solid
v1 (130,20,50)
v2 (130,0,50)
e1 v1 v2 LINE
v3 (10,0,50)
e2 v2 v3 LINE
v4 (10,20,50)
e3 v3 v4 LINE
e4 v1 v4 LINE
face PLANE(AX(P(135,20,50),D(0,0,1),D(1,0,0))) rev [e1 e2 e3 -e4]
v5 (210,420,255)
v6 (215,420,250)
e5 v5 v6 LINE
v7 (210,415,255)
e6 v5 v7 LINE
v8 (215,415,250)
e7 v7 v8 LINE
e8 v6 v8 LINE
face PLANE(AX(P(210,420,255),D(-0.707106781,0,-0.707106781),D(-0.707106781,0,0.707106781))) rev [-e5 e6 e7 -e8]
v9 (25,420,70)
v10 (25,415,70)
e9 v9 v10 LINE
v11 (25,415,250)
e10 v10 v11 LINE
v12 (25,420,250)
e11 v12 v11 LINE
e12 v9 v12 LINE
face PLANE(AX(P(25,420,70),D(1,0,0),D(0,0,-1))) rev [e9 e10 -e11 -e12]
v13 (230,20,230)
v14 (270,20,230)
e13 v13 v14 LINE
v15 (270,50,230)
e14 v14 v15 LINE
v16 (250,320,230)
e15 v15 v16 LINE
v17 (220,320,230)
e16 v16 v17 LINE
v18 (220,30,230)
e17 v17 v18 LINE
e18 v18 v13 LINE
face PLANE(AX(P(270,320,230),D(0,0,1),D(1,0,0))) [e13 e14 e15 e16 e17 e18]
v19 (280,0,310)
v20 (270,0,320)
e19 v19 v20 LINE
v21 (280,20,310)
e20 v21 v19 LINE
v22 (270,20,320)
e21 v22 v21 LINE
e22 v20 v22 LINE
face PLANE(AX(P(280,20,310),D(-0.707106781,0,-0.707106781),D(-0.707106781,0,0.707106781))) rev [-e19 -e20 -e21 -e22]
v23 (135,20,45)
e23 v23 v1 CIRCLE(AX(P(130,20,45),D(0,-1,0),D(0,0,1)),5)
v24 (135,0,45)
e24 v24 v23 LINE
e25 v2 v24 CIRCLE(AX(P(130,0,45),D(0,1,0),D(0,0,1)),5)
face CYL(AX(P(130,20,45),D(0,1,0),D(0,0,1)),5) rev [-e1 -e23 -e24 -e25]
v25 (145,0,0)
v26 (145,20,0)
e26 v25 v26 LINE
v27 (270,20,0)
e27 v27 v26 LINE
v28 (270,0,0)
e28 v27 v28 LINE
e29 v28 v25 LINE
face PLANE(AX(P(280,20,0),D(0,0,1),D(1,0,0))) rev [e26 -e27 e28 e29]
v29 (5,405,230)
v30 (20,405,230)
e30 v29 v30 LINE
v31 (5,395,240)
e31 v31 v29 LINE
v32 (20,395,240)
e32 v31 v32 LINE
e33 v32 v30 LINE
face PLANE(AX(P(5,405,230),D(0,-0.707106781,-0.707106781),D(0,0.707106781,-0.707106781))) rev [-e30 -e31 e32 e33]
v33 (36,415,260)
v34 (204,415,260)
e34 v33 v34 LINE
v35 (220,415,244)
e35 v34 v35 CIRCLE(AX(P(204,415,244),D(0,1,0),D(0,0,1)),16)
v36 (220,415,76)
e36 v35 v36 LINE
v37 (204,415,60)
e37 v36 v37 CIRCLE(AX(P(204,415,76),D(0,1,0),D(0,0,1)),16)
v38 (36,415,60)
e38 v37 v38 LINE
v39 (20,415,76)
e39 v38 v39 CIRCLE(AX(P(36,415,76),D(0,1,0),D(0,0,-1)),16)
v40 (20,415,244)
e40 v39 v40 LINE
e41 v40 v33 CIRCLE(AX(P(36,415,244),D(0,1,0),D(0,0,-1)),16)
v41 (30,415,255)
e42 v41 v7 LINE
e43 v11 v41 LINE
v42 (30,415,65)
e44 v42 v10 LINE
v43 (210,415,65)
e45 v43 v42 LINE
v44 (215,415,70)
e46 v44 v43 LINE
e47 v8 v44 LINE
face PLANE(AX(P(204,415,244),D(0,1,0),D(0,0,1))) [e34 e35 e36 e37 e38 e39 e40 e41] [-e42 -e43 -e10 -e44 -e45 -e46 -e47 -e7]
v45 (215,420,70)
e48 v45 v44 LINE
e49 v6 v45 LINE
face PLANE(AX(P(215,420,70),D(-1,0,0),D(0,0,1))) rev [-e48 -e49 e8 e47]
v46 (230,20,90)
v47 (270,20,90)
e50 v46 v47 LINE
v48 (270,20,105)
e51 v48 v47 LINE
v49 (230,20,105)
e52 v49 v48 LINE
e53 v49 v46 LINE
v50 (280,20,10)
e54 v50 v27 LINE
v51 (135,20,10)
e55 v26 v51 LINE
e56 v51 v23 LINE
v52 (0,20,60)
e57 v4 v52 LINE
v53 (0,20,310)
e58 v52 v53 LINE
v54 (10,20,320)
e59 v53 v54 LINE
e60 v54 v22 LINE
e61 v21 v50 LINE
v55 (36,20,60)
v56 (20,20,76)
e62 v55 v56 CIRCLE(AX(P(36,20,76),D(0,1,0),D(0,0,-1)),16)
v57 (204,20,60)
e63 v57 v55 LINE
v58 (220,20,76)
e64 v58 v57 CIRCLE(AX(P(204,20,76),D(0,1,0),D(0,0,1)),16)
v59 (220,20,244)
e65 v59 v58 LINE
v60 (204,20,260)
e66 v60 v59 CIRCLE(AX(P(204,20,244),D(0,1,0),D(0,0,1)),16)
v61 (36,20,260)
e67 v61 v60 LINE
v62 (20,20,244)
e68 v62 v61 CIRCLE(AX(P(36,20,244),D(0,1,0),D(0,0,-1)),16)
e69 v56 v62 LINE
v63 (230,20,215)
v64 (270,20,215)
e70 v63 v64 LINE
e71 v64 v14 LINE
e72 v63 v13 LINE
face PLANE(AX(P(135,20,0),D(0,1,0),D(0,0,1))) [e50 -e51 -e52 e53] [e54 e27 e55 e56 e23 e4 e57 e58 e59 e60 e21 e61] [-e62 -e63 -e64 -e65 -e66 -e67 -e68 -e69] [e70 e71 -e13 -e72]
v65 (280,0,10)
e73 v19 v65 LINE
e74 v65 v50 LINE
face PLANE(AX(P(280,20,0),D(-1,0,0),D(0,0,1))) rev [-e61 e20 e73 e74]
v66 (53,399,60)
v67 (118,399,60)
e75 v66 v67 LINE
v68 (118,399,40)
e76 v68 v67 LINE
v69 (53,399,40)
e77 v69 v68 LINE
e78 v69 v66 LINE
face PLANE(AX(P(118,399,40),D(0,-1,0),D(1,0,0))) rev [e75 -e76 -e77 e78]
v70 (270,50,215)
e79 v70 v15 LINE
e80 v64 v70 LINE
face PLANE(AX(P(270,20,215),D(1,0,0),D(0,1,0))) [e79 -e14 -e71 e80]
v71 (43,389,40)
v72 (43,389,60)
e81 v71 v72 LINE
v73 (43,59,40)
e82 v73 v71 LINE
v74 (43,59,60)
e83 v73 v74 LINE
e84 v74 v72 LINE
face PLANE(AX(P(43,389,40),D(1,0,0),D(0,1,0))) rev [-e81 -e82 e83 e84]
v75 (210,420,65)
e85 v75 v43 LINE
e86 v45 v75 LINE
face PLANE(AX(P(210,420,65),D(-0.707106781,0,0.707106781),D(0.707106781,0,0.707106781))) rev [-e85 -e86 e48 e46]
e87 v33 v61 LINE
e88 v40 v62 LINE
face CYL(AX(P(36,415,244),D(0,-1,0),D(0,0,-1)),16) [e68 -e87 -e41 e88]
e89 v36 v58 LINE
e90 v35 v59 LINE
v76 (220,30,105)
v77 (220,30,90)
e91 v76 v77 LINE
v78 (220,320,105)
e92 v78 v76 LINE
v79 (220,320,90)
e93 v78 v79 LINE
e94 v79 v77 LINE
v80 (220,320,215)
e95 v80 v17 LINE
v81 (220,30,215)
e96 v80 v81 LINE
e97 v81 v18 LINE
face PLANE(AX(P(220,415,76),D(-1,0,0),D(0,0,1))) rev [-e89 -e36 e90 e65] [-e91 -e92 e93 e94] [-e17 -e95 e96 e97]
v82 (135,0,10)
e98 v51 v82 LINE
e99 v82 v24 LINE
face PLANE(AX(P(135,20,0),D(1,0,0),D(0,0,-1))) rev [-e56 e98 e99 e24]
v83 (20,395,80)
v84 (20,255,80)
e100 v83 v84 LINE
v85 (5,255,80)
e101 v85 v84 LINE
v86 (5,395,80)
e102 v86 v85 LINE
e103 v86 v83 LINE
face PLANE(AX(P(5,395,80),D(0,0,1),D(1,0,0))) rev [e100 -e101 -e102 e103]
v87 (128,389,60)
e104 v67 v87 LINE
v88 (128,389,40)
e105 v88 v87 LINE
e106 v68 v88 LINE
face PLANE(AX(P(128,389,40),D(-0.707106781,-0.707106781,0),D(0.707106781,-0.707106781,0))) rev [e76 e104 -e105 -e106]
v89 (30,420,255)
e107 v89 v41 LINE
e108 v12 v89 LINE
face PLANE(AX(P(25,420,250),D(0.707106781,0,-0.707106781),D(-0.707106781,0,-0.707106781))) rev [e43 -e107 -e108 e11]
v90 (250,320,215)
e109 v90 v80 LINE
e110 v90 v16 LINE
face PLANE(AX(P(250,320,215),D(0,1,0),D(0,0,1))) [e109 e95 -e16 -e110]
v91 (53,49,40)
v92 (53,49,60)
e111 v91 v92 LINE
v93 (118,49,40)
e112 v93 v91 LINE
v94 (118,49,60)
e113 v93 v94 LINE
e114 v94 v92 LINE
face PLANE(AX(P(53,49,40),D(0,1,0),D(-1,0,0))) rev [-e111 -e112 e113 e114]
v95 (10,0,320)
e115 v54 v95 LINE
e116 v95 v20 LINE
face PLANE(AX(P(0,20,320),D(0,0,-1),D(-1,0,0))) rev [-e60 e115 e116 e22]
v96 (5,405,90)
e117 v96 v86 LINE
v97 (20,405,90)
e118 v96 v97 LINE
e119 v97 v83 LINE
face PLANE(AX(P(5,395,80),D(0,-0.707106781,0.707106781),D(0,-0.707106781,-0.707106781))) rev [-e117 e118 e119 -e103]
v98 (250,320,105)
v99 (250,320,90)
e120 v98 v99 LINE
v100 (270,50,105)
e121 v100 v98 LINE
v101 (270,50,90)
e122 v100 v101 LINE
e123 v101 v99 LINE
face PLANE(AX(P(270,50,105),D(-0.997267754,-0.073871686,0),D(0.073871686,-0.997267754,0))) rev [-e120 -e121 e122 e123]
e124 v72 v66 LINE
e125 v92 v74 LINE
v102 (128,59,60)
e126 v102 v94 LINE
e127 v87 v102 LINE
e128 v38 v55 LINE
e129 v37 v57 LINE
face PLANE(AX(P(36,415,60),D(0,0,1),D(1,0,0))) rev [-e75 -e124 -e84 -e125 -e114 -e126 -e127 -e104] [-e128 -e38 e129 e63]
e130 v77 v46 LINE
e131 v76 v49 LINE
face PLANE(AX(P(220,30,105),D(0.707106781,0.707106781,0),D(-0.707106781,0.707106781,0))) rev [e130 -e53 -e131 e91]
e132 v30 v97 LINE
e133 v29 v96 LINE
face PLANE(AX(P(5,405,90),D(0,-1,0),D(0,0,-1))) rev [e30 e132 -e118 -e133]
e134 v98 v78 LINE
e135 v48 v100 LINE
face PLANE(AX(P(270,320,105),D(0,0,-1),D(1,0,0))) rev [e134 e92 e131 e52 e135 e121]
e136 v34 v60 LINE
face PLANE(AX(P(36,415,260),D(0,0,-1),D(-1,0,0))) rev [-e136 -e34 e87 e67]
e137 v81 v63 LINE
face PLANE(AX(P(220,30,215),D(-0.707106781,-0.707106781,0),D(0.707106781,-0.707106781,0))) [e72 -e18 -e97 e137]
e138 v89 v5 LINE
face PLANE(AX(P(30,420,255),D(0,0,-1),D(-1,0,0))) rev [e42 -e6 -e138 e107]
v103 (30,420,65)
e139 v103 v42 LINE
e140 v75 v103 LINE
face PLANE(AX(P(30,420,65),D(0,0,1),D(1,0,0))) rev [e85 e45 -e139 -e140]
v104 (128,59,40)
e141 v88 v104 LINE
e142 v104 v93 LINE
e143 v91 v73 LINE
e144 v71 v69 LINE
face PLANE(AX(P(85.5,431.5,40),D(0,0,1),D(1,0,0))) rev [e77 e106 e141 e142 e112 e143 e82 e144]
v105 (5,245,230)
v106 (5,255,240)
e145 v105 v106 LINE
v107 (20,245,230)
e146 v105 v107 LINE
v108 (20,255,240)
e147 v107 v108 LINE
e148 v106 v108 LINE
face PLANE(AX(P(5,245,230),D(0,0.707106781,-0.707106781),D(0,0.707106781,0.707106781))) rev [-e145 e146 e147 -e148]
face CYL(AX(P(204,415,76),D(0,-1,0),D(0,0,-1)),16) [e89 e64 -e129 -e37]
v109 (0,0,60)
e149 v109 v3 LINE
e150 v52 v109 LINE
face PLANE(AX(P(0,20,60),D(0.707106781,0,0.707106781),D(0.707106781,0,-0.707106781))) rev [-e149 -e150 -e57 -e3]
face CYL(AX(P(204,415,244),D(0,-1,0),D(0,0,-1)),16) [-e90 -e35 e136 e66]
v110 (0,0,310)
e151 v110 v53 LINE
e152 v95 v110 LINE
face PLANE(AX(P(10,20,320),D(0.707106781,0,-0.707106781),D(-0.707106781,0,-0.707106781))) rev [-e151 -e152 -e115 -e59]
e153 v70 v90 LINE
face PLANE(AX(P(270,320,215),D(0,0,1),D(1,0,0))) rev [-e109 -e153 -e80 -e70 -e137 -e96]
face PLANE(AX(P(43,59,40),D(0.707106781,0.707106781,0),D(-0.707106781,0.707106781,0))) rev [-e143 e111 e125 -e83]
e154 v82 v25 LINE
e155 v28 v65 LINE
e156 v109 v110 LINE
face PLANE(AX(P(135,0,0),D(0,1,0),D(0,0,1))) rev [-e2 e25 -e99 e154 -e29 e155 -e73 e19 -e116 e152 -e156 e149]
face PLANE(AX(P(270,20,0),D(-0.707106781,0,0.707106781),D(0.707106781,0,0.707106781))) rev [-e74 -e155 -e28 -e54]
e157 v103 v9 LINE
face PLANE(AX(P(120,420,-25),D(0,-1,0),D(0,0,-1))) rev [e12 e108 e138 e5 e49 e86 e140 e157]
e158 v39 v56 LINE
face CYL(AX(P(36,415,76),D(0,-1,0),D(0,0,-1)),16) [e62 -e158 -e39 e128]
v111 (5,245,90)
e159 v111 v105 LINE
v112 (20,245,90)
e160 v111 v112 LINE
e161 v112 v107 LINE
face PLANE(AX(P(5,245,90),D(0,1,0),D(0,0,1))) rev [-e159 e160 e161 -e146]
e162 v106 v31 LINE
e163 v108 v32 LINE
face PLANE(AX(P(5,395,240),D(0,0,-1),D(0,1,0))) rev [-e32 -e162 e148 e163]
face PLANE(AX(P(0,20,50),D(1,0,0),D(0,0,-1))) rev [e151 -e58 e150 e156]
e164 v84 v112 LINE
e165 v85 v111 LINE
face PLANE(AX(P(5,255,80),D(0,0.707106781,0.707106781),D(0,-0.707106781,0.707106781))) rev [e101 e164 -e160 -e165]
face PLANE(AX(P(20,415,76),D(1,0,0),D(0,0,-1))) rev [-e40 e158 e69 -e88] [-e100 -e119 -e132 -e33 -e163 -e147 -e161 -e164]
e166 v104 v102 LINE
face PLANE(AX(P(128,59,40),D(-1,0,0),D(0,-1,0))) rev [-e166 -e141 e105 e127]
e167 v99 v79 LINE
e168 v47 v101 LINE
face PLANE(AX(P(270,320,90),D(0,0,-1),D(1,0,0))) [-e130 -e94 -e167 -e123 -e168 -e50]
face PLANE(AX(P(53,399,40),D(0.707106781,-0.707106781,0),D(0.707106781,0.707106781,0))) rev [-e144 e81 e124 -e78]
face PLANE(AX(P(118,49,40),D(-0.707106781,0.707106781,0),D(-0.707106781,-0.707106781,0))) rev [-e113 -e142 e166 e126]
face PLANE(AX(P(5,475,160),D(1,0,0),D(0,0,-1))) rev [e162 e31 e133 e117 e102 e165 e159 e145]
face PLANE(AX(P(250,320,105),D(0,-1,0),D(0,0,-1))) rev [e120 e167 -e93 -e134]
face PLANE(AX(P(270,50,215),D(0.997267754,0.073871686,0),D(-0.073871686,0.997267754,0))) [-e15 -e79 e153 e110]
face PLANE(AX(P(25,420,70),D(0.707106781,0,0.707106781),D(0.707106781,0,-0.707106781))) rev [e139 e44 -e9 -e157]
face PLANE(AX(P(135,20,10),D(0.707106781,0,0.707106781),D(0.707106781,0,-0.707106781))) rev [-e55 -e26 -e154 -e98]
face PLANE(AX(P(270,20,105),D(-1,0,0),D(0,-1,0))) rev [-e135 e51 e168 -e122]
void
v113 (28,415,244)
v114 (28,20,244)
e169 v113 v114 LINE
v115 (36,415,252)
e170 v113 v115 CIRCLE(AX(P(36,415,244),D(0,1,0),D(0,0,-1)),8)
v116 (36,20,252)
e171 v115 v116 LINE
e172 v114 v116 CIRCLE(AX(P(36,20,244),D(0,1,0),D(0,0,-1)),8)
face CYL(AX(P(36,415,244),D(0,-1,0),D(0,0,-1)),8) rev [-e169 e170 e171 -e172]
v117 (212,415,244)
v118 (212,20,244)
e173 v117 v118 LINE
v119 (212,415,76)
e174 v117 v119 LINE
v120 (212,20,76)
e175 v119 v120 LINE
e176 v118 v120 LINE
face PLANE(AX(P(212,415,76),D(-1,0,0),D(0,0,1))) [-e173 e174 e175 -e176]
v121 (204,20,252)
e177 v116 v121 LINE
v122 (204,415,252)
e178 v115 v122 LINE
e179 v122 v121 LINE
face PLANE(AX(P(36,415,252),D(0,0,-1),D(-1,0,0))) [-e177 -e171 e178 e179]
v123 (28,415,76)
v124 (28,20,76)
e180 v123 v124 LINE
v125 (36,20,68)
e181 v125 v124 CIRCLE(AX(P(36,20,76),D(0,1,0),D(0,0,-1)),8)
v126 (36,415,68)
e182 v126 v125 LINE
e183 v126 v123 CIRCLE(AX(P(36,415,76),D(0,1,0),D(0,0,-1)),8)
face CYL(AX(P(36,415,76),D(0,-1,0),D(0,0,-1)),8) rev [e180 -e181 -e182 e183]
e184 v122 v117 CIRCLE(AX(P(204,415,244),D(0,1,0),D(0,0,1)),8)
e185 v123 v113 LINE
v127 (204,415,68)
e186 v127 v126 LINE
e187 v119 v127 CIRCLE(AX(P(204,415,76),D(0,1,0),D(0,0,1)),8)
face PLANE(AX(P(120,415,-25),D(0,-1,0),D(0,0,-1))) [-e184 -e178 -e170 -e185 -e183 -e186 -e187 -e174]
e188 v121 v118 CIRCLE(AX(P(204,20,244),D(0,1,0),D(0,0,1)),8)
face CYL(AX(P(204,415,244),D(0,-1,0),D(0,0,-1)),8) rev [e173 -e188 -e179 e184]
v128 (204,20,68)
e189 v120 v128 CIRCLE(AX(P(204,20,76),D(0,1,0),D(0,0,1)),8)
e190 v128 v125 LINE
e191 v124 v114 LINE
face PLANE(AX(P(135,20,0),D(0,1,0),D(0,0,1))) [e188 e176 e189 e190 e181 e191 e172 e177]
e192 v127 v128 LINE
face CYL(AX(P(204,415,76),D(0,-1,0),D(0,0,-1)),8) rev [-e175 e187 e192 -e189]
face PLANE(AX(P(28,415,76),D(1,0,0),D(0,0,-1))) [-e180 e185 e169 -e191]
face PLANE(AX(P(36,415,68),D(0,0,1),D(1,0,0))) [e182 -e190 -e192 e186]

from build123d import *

# Parameters (mm, degrees)
BOSS_EXTRUDE1_DEPTH = 20
BOSS_EXTRUDE2_DEPTH = 395
BOSS_EXTRUDE3_START = -30
BOSS_EXTRUDE3_DEPTH = 15
BOSS_EXTRUDE4_DEPTH = 5
BOSS_EXTRUDE5_DEPTH = 15
CHAMFER1_SIZE       = 10
BOSS_EXTRUDE8_DEPTH = 20
FILLET1_R           = 5
CHAMFER2_SIZE       = 10


with BuildPart() as part:
    # Sketch1 → Boss-Extrude1 (new body)
    with BuildSketch(Plane(origin=(0, 0, 0), x_dir=(1, 0, 0), z_dir=(0, 1, 0))):
        Polygon((280, 0), (280, -320), (0, -320), (0, -50), (135, -50), (135, 0), align=None)
    extrude(amount=BOSS_EXTRUDE1_DEPTH)

    # Sketch2 → Boss-Extrude2 (add)
    with BuildSketch(Plane(origin=(0, 20, 0), x_dir=(1, 0, 0), z_dir=(0, 1, 0))):
        with BuildLine():
            Line((36, -60), (204, -60))
            ThreePointArc((204, -60), (215.313708499, -64.686291501), (220, -76))
            Line((220, -76), (220, -244))
            ThreePointArc((220, -244), (215.313708499, -255.313708499), (204, -260))
            Line((204, -260), (36, -260))
            ThreePointArc((36, -260), (24.686291501, -255.313708499), (20, -244))
            Line((20, -244), (20, -76))
            ThreePointArc((20, -76), (24.686291501, -64.686291501), (36, -60))
        make_face()
        with BuildLine():
            Line((36, -68), (204, -68))
            ThreePointArc((204, -68), (209.656854249, -70.343145751), (212, -76))
            Line((212, -76), (212, -244))
            ThreePointArc((212, -244), (209.656854249, -249.656854249), (204, -252))
            Line((204, -252), (36, -252))
            ThreePointArc((36, -252), (30.343145751, -249.656854249), (28, -244))
            Line((28, -244), (28, -76))
            ThreePointArc((28, -76), (30.343145751, -70.343145751), (36, -68))
        make_face(mode=Mode.SUBTRACT)
    extrude(amount=BOSS_EXTRUDE2_DEPTH)

    # Sketch3 → Boss-Extrude3 (add)
    with BuildSketch(Plane.XY.offset(260).offset(BOSS_EXTRUDE3_START)):
        Polygon((230, 20), (270, 20), (270, 50), (250, 320), (220, 320), (220, 30), align=None)
    boss_extrude3 = extrude(amount=-BOSS_EXTRUDE3_DEPTH)

    # Mirror1: Boss-Extrude3 across plane
    add(boss_extrude3.mirror(Plane(origin=(0, 0, 160), x_dir=(1, 0, 0), z_dir=(0, 0, -1))))

    # Sketch4 → Boss-Extrude4 (add)
    with BuildSketch(Plane(origin=(0, 415, 0), x_dir=(1, 0, 0), z_dir=(0, 1, 0))):
        Polygon((30, -65), (210, -65), (215, -70), (215, -250), (210, -255), (30, -255), (25, -250), (25, -70), align=None)
    extrude(amount=BOSS_EXTRUDE4_DEPTH)

    # Sketch5 → Boss-Extrude5 (add)
    with BuildSketch(Plane.ZY.offset(-20)):
        Polygon((90, 405), (230, 405), (240, 395), (240, 255), (230, 245), (90, 245), (80, 255), (80, 395), align=None)
    extrude(amount=BOSS_EXTRUDE5_DEPTH)

    # Chamfer1
    chamfer1_edges = [part.edges().sort_by_distance(p)[0] for p in [
        (280, 10, 0),
        (280, 10, 320),
        (0, 10, 320),
        (0, 10, 50),
    ]]
    chamfer(chamfer1_edges, length=CHAMFER1_SIZE)

    # Sketch8 → Boss-Extrude8 (add)
    with BuildSketch(Plane(origin=(0, 0, 60), x_dir=(-1, 0, 0), z_dir=(0, 0, -1))):
        Polygon((-118, 399), (-53, 399), (-43, 389), (-43, 59), (-53, 49), (-118, 49), (-128, 59), (-128, 389), align=None)
    extrude(amount=BOSS_EXTRUDE8_DEPTH)

    # Fillet1
    fillet1_edges = [part.edges().sort_by_distance(p)[0] for p in [
        (135, 10, 50),
    ]]
    fillet(fillet1_edges, radius=FILLET1_R)

    # Chamfer2
    chamfer2_edges = [part.edges().sort_by_distance(p)[0] for p in [
        (135, 10, 0),
    ]]
    chamfer(chamfer2_edges, length=CHAMFER2_SIZE)


solid = part.part
